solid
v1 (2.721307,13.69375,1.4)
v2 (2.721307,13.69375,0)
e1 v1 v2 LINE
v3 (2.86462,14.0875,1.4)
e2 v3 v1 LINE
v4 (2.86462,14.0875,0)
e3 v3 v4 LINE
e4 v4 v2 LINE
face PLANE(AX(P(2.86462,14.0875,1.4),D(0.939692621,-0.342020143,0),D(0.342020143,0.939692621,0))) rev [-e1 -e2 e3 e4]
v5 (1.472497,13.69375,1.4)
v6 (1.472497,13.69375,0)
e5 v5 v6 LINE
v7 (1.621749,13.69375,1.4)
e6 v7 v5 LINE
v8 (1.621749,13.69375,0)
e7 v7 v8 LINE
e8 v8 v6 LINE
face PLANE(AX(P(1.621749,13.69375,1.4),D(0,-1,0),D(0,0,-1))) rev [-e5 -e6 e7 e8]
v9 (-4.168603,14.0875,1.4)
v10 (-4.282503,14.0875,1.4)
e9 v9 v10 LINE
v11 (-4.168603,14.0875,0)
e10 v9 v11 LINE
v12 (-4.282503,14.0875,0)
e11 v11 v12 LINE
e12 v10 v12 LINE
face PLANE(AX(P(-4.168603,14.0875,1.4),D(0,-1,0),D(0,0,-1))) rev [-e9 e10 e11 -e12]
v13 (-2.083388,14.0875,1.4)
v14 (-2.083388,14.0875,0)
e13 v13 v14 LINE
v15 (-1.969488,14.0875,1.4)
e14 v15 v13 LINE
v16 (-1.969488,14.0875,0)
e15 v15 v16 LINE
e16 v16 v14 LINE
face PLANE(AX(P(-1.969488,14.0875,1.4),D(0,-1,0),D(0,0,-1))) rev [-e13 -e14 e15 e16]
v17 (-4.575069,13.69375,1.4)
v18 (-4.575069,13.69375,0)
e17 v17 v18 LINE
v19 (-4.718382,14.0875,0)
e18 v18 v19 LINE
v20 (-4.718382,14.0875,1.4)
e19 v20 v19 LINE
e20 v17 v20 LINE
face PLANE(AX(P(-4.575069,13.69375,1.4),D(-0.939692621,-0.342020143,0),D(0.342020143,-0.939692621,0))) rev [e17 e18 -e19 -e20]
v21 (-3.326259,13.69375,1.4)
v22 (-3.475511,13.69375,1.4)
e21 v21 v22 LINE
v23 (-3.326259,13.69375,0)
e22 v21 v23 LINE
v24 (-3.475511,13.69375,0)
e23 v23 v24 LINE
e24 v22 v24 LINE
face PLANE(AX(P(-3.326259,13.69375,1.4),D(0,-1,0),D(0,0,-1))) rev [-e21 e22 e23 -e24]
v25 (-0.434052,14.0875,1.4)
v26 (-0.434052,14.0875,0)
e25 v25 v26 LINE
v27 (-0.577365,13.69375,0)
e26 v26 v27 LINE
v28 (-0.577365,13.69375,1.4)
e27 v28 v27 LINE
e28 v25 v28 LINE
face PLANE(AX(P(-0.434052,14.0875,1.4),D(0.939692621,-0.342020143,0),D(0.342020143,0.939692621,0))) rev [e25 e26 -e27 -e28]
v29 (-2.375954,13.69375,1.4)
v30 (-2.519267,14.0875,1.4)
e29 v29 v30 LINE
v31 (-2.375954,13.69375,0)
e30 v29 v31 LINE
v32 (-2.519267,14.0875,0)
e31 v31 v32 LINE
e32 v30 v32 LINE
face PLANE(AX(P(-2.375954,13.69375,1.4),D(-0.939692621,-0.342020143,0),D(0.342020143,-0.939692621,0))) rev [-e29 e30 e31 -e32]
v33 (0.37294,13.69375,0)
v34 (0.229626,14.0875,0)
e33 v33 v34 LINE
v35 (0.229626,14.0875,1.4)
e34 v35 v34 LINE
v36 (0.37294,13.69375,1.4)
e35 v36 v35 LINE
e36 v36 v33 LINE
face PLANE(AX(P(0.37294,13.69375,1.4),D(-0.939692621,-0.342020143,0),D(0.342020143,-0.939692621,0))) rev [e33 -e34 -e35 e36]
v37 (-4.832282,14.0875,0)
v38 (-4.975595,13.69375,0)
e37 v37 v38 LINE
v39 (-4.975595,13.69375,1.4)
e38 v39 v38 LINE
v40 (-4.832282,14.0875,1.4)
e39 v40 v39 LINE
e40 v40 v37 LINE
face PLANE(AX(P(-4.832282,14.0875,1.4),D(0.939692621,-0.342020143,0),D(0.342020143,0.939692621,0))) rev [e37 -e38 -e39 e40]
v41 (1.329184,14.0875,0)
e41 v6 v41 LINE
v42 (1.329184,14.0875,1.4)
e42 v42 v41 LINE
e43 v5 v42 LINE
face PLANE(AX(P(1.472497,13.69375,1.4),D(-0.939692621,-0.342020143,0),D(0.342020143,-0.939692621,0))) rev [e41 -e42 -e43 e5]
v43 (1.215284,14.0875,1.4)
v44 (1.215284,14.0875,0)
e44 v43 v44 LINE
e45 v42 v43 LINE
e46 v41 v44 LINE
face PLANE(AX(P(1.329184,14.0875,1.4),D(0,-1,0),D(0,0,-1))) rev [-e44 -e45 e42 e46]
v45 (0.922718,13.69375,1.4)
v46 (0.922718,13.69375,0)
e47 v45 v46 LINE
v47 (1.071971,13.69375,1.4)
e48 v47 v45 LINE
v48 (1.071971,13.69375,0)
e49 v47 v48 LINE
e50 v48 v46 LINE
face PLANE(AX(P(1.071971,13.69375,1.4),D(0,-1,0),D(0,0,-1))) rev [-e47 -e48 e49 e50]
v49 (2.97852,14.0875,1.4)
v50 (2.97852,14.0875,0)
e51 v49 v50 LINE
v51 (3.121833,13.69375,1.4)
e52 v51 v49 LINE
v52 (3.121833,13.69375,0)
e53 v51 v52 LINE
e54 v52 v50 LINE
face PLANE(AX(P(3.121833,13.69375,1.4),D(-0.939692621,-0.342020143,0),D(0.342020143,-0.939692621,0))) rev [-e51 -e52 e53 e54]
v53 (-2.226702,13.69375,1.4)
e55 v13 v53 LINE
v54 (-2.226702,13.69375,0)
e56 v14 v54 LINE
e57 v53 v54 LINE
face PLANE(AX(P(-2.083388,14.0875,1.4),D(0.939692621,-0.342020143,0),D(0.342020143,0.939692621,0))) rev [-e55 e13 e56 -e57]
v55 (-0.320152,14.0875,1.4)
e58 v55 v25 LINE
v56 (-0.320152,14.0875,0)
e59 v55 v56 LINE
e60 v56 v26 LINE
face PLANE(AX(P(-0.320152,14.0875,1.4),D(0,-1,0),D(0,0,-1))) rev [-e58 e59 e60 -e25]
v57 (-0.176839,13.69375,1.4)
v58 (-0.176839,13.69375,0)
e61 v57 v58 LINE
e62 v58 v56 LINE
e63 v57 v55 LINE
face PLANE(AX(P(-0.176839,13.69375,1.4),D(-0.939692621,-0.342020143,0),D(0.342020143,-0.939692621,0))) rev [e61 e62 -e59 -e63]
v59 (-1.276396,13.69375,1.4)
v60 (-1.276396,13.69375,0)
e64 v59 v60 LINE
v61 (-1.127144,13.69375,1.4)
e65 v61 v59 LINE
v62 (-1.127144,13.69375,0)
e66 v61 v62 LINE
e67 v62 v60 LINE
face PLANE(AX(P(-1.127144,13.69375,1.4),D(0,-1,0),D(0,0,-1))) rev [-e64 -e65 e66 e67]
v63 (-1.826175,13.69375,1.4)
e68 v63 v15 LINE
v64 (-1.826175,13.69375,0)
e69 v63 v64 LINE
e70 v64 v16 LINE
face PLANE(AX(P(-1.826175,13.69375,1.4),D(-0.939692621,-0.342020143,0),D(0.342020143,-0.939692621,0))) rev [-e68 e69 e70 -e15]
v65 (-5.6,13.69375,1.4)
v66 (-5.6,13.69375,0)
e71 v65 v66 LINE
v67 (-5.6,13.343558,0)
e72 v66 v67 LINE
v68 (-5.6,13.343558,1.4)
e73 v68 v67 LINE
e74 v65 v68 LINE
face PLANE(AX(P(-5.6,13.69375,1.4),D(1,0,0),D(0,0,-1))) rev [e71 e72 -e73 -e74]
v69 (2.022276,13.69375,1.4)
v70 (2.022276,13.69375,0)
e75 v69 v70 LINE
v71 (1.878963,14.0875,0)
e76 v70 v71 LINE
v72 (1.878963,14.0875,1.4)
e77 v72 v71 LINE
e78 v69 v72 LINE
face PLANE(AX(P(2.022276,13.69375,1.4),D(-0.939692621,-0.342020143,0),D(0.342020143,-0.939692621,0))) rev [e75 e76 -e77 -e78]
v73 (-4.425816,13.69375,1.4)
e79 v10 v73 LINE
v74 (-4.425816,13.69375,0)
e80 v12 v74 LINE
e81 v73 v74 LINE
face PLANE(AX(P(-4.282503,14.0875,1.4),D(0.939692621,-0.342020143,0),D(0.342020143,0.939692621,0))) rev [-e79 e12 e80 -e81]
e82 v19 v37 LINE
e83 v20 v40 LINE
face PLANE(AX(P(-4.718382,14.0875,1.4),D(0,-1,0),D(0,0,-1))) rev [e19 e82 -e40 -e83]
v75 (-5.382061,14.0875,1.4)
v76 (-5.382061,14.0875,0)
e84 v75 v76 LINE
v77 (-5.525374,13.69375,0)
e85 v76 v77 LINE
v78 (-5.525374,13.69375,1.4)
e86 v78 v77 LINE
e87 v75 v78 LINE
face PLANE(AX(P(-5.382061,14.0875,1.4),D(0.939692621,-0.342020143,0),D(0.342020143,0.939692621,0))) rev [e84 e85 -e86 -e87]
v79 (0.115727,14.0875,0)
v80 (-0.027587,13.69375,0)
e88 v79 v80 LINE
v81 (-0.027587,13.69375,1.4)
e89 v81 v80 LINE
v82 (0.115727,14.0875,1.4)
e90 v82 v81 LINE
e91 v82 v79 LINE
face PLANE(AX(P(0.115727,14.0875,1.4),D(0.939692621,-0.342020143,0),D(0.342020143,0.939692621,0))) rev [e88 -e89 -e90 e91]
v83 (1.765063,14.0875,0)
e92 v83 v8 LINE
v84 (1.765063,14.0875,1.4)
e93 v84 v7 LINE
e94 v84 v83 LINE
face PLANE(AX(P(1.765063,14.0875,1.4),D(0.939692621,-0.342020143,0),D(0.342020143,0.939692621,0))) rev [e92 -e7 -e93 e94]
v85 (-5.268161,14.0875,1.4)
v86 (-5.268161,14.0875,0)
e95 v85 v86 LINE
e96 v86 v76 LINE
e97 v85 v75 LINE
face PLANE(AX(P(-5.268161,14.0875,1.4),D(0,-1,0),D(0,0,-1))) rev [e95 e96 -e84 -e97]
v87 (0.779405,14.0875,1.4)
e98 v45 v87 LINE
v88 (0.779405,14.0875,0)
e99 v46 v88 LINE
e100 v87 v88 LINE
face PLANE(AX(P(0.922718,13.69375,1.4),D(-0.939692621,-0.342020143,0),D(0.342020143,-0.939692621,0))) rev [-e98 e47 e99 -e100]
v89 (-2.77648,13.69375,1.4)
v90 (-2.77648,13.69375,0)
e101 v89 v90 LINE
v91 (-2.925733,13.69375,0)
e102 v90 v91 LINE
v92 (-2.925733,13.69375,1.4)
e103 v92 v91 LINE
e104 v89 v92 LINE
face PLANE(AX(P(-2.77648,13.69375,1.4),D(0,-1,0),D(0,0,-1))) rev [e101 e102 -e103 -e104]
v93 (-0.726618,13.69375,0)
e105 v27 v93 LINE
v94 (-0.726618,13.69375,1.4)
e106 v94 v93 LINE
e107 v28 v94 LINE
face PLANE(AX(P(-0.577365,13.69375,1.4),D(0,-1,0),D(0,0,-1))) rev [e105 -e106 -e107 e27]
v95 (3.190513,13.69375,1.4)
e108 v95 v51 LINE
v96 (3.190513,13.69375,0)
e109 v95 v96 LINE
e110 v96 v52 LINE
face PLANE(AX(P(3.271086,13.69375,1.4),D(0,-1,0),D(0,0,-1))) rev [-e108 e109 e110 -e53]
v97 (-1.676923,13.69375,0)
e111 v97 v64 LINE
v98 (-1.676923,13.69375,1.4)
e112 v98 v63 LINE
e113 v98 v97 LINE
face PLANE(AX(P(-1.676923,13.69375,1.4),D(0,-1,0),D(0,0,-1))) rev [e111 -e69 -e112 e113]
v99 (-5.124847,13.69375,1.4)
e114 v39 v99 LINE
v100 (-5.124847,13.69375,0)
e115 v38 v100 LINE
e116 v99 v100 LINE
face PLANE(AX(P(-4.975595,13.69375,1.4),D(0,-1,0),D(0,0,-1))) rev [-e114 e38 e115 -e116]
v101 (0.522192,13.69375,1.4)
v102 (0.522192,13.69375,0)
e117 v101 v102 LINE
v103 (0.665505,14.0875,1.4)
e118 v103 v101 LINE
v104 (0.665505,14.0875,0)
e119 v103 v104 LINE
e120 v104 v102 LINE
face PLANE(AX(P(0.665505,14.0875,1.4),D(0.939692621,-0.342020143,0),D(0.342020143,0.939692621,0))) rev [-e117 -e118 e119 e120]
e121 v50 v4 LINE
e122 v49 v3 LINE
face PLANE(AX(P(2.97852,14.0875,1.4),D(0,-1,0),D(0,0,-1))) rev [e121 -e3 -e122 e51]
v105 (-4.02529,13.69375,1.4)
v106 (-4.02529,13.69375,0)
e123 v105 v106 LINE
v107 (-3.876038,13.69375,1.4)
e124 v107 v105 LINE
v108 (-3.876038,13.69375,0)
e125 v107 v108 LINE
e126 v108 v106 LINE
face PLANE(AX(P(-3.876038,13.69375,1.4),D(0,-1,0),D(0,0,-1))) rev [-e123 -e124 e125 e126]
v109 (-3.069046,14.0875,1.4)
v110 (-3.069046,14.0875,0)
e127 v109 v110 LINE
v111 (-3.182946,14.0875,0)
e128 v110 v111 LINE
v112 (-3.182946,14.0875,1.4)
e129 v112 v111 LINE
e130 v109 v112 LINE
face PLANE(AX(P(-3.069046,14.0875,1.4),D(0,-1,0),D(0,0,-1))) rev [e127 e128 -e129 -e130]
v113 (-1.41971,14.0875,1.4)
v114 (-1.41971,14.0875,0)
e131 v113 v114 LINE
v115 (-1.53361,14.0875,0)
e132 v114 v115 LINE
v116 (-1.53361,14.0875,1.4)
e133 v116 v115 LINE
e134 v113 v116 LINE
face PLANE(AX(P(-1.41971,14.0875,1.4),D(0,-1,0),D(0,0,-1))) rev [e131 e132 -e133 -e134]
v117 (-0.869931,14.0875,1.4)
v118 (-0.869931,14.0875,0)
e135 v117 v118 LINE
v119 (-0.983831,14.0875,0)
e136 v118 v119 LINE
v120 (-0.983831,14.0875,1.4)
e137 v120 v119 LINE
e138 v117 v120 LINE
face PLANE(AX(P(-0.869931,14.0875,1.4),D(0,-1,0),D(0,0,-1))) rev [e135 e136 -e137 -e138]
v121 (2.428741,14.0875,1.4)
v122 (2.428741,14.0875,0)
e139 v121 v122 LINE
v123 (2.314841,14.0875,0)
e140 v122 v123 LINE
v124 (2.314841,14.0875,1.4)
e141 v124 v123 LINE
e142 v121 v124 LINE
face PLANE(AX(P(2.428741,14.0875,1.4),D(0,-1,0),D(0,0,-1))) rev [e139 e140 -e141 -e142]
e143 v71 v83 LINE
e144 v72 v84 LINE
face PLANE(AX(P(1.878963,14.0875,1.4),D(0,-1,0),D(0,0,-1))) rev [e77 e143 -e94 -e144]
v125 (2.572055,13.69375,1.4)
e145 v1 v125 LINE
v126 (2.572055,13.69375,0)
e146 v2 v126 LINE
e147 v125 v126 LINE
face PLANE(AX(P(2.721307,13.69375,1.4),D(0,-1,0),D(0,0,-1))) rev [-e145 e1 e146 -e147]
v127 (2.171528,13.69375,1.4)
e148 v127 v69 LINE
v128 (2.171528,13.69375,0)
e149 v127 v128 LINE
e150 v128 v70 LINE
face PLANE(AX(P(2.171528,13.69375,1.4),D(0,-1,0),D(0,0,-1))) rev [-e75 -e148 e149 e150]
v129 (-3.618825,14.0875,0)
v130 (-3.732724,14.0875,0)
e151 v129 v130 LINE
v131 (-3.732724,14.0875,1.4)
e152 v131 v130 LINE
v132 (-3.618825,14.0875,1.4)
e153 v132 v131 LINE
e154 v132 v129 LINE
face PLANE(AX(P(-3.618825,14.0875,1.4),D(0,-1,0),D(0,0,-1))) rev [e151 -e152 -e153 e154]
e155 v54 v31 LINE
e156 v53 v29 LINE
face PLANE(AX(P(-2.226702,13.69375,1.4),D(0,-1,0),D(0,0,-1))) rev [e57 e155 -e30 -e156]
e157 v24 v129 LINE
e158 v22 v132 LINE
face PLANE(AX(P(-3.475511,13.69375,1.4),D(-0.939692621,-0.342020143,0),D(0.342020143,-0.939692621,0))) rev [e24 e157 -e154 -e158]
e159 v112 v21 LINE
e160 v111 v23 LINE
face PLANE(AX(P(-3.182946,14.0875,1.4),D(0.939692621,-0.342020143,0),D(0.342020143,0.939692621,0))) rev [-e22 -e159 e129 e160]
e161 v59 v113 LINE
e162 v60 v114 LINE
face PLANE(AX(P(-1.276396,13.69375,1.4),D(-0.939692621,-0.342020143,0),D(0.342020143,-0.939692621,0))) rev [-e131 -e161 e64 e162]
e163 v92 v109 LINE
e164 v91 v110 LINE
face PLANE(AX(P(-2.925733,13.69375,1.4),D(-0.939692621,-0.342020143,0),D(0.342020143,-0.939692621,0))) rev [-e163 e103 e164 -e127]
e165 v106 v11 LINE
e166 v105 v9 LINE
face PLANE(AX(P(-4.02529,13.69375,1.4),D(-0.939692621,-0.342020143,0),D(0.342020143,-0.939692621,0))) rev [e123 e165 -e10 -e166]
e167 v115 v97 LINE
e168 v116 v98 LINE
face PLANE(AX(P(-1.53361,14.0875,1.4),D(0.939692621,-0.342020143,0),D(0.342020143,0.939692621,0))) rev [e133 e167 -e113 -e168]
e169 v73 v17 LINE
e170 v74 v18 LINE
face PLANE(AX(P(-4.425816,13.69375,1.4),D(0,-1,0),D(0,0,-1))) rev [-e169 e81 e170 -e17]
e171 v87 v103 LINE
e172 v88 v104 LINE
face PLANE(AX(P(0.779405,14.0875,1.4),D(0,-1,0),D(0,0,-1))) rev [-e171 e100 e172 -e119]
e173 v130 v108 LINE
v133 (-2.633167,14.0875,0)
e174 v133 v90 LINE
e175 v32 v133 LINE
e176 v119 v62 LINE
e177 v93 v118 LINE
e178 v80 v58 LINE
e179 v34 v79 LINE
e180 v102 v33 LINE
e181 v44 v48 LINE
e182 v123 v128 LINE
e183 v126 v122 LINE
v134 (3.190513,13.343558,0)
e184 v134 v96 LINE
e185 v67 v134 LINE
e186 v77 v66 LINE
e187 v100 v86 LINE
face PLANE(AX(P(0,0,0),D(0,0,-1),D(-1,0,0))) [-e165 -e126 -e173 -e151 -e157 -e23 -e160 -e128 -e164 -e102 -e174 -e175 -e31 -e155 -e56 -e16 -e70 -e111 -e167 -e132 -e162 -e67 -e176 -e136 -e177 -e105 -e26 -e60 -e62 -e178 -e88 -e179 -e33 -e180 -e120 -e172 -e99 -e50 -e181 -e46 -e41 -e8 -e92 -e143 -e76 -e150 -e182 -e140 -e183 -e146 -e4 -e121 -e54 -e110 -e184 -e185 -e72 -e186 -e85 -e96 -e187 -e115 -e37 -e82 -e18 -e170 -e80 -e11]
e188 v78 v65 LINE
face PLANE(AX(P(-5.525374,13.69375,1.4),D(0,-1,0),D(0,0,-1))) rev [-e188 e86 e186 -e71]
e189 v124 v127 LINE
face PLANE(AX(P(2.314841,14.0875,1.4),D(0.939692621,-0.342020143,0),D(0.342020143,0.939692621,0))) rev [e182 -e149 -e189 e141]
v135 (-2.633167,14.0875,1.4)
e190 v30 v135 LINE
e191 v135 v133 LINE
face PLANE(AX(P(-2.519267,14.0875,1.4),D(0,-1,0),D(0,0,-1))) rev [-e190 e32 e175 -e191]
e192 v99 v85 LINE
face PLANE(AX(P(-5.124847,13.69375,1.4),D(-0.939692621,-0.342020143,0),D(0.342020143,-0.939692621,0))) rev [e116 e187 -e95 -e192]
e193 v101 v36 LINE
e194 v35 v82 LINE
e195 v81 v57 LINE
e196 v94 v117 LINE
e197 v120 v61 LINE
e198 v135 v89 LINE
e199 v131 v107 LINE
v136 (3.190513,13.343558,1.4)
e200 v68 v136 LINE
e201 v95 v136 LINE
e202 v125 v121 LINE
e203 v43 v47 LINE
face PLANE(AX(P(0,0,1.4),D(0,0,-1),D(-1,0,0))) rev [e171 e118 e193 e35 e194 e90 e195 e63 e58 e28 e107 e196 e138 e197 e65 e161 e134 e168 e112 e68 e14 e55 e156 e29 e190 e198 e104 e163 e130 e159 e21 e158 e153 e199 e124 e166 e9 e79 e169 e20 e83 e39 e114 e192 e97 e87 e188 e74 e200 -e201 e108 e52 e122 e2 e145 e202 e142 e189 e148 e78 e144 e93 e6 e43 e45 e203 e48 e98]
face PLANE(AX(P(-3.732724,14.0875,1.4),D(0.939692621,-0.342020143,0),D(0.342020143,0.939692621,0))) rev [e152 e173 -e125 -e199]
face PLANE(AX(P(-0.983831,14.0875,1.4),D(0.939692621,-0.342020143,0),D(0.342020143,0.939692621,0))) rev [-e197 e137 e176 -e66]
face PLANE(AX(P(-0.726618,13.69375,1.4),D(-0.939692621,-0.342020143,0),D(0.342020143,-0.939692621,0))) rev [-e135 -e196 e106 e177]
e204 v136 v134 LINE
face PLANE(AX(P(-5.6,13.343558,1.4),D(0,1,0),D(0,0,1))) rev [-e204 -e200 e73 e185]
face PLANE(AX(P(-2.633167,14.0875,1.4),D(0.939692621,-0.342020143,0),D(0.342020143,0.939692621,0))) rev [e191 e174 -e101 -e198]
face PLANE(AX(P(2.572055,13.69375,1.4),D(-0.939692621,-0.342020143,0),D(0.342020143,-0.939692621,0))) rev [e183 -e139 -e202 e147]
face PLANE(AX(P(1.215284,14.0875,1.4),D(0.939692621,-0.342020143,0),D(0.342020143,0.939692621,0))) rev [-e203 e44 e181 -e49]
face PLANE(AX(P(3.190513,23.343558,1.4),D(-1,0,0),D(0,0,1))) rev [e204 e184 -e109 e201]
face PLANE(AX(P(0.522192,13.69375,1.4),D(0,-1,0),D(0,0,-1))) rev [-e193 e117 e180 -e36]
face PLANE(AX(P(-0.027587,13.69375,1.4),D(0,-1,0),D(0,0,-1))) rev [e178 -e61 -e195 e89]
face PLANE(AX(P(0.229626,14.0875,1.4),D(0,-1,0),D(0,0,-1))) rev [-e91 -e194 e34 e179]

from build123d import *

# Parameters (mm, degrees)
BOSS_EXTRUDE1_DEPTH = 2
SCALE_1_SCALE       = 0.7
SKETCH2_W           = 2.409487025
SKETCH2_H           = 1.4
CUT_EXTRUDE1_DEPTH  = 10


with BuildPart() as part:
    # Sketch1 → Boss-Extrude1 (new body)
    with BuildSketch(Plane.XY):
        Polygon((7.814572092, 19.5625), (7.601354408, 19.5625), (7.396621151, 20.125), (7.233907187, 20.125), (7.02917393, 19.5625), (6.815956245, 19.5625), (6.611222988, 20.125), (6.448509024, 20.125), (6.243775767, 19.5625), (6.030558083, 19.5625), (5.825824826, 20.125), (5.663110862, 20.125), (5.458377605, 19.5625), (5.24515992, 19.5625), (5.040426663, 20.125), (4.877712699, 20.125), (4.672979442, 19.5625), (4.459761758, 19.5625), (4.255028501, 20.125), (4.092314537, 20.125), (3.88758128, 19.5625), (3.674363595, 19.5625), (3.469630338, 20.125), (3.306916374, 20.125), (3.102183117, 19.5625), (2.888965433, 19.5625), (2.684232176, 20.125), (2.521518212, 20.125), (2.316784955, 19.5625), (2.10356727, 19.5625), (1.898834013, 20.125), (1.736120049, 20.125), (1.531386792, 19.5625), (1.318169108, 19.5625), (1.113435851, 20.125), (0.950721887, 20.125), (0.74598863, 19.5625), (0.532770945, 19.5625), (0.328037688, 20.125), (0.165323724, 20.125), (-0.039409533, 19.5625), (-0.252627217, 19.5625), (-0.457360474, 20.125), (-0.620074438, 20.125), (-0.824807695, 19.5625), (-1.03802538, 19.5625), (-1.242758637, 20.125), (-1.405472601, 20.125), (-1.610205858, 19.5625), (-1.823423542, 19.5625), (-2.028156799, 20.125), (-2.190870763, 20.125), (-2.39560402, 19.5625), (-2.608821705, 19.5625), (-2.813554962, 20.125), (-2.976268926, 20.125), (-3.181002183, 19.5625), (-3.394219867, 19.5625), (-3.598953124, 20.125), (-3.761667088, 20.125), (-3.966400345, 19.5625), (-4.17961803, 19.5625), (-4.384351287, 20.125), (-4.547065251, 20.125), (-4.751798508, 19.5625), (-4.965016192, 19.5625), (-5.169749449, 20.125), (-5.332463413, 20.125), (-5.53719667, 19.5625), (-5.750414355, 19.5625), (-5.955147612, 20.125), (-6.117861576, 20.125), (-6.322594833, 19.5625), (-6.535812517, 19.5625), (-6.740545774, 20.125), (-6.903259738, 20.125), (-7.107992995, 19.5625), (-7.32121068, 19.5625), (-7.525943937, 20.125), (-7.688657901, 20.125), (-7.893391158, 19.5625), (-8, 19.5625), (-8, 19.062226191), (8, 19.062226191), (8, 20.071958989), align=None)
    extrude(amount=BOSS_EXTRUDE1_DEPTH)


with BuildPart() as part_1:
    # Scale 1: scaled about (0, 0, 0)
    add(part.part.scale(SCALE_1_SCALE))

    # Sketch2 → Cut-Extrude1 (cut)
    with BuildSketch(Plane(origin=(0, 13.343558334, 0), x_dir=(-1, 0, 0), z_dir=(0, -1, 0))):
        with Locations((-4.395256488, -0.7)):
            Rectangle(SKETCH2_W, SKETCH2_H)
    extrude(amount=-CUT_EXTRUDE1_DEPTH, mode=Mode.SUBTRACT)


solid = part_1.part
